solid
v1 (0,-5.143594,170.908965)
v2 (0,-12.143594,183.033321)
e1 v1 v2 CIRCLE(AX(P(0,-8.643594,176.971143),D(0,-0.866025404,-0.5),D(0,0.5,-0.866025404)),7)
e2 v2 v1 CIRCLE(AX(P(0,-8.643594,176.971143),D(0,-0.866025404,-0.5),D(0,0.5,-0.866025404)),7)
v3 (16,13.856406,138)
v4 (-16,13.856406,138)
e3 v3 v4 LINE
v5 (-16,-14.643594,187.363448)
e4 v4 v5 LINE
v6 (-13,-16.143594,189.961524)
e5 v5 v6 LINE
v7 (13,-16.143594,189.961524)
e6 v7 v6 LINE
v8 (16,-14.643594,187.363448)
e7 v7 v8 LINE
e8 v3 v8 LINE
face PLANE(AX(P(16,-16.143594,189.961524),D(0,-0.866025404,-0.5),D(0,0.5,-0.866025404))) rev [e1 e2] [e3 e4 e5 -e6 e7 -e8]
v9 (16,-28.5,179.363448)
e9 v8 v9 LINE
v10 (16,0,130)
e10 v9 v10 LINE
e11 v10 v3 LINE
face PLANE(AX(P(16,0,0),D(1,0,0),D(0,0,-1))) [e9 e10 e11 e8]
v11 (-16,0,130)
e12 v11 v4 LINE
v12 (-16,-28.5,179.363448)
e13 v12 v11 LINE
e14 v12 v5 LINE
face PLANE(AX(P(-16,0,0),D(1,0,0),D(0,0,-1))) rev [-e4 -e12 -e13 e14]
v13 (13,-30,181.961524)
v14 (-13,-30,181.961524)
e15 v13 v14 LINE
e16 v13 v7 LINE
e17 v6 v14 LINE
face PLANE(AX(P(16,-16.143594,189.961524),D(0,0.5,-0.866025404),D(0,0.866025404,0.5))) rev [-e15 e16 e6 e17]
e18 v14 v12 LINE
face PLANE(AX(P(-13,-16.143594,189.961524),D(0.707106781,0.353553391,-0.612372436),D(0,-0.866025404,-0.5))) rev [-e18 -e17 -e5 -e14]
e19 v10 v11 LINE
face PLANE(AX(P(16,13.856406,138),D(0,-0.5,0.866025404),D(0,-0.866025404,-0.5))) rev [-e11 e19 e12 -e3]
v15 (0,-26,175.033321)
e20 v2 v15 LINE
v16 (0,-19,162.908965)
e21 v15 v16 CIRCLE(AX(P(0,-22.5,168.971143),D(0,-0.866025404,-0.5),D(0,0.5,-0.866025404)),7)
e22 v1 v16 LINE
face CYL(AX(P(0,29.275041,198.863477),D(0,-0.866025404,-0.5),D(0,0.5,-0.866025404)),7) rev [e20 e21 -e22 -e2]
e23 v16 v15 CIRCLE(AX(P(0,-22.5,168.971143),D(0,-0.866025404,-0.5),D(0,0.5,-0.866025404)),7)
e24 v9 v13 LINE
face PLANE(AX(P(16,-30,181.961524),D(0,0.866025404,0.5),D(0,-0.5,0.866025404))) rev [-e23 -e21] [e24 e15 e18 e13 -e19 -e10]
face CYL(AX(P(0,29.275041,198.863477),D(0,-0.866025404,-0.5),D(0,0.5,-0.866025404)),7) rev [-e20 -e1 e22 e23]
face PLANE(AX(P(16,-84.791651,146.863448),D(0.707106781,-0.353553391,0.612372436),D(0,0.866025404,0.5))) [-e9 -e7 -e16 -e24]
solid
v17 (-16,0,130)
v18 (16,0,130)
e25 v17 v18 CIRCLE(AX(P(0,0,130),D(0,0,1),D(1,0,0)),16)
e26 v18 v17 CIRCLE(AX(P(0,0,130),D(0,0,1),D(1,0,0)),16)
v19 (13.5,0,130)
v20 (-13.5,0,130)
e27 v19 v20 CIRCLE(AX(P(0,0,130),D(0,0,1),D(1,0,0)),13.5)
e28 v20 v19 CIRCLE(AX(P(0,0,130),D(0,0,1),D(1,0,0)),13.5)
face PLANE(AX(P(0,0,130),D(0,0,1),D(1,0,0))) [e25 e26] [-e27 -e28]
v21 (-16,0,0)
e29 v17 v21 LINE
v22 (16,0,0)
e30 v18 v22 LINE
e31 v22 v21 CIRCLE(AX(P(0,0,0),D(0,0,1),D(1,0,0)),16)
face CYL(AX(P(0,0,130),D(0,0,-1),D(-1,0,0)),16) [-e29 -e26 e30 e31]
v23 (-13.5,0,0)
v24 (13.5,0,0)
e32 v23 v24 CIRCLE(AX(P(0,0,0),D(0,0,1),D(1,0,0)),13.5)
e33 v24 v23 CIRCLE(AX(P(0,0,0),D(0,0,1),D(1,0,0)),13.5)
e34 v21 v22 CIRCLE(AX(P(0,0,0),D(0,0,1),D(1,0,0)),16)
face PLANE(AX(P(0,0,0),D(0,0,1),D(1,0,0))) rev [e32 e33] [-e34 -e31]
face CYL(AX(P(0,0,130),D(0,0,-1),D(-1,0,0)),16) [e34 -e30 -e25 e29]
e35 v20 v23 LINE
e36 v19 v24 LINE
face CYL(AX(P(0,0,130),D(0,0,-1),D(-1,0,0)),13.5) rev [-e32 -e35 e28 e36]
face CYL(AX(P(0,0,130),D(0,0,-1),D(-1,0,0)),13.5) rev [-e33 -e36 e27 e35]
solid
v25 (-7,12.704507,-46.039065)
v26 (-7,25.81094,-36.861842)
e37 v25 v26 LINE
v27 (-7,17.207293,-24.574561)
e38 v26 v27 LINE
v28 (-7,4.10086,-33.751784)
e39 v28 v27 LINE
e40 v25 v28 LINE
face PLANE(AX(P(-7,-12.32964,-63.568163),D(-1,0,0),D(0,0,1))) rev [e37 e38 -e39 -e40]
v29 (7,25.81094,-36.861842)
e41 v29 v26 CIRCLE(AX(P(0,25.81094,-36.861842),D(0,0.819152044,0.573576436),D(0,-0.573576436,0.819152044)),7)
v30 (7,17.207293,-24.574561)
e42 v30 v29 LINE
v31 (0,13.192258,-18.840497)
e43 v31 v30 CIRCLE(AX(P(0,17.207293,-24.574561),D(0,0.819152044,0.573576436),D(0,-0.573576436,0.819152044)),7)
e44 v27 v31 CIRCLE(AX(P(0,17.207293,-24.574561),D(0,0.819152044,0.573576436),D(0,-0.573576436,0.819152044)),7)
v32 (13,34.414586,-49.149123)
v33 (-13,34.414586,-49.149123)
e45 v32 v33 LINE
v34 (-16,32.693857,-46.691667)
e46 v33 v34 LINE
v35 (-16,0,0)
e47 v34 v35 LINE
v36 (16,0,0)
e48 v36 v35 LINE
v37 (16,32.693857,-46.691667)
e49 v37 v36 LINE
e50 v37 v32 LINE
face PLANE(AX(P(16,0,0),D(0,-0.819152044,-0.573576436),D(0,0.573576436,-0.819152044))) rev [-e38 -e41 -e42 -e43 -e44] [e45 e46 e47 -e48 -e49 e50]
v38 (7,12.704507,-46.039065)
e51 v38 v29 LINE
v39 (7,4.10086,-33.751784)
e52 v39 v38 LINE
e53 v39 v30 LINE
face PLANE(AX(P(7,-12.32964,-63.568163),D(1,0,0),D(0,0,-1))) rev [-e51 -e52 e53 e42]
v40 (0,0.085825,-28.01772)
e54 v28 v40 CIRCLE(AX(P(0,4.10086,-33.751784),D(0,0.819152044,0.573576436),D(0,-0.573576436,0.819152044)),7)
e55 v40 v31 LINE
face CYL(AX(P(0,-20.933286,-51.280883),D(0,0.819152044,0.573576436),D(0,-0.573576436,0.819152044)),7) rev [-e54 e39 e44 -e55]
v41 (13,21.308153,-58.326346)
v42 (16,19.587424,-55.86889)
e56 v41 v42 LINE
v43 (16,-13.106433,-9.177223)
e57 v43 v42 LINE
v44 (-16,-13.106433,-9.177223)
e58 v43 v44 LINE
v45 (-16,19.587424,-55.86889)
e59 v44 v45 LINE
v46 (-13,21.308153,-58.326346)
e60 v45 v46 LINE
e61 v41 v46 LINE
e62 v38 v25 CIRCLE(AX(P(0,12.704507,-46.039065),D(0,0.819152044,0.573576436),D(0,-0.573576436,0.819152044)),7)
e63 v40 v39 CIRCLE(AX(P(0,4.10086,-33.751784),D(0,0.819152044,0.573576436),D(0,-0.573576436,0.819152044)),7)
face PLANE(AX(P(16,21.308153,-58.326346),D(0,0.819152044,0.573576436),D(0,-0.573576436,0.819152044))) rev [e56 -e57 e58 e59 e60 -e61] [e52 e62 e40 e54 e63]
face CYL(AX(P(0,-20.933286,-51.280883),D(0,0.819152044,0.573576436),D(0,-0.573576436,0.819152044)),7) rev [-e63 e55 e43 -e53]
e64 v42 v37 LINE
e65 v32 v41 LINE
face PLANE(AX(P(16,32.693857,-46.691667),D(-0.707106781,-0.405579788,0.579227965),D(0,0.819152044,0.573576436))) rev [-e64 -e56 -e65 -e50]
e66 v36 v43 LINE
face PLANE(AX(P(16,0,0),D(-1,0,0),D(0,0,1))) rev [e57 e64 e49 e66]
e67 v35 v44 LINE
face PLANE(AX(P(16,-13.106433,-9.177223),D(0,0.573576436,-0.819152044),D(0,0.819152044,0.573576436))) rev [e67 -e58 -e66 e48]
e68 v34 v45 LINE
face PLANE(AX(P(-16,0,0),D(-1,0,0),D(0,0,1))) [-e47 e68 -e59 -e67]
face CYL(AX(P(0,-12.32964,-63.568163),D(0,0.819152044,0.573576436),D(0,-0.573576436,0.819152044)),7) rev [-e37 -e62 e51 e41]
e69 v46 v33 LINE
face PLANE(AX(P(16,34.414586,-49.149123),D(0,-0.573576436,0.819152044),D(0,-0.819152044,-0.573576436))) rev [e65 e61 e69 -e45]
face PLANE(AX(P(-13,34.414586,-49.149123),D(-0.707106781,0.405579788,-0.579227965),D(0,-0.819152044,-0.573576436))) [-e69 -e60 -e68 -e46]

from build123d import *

# Parameters (mm, degrees)
SKETCH_1_R          = 16
SKETCH_1_R_2        = 13.5
EXTRUDE_1_DEPTH     = 130
EXTRUDE_2_DEPTH     = 16
CUT_EXTRUDE_1_DEPTH = 136.426599093
EXTRUDE_3_DEPTH     = 16
SKETCH_5_R          = 7
CUT_EXTRUDE_2_DEPTH = 181.267525325
CHAMFER_1_SIZE      = 3
CHAMFER_2_SIZE      = 3


with BuildPart() as part:
    # 草图1 → 凸台-拉伸1 (new body)
    with BuildSketch(Plane.XY):
        Circle(SKETCH_1_R)
        Circle(SKETCH_1_R_2, mode=Mode.SUBTRACT)
    extrude(amount=EXTRUDE_1_DEPTH)


with BuildPart() as body_2:
    # 草图2 → 凸台-拉伸2 (new, symmetric)
    with BuildSketch(Plane(origin=(0, 0, 0), x_dir=(0, 0, -1), z_dir=(1, 0, 0))):
        Polygon((0, 0), (49.149122657, 34.414586181), (58.326345639, 21.308153472), (9.177222982, -13.106432709), align=None)
    extrude(amount=EXTRUDE_2_DEPTH, both=True)

    # 草图3 → 切除-拉伸1 (cut, through all)
    with BuildSketch(Plane(origin=(0, 0, 0), x_dir=(1, 0, 0), z_dir=(0, 0.8191520442889908, 0.5735764363510477))):
        with BuildLine():
            Line((7, 45), (7, 30))
            ThreePointArc((7, 30), (0, 23), (-7, 30))
            Line((-7, 30), (-7, 45))
            ThreePointArc((-7, 45), (0, 52), (7, 45))
        make_face()
    extrude(amount=-CUT_EXTRUDE_1_DEPTH, mode=Mode.SUBTRACT)

    # 倒角2
    chamfer_2_edges = [body_2.edges().sort_by_distance(p)[0] for p in [
        (16, 27.861369827, -53.737734148),
        (-16, 27.861369827, -53.737734148),
    ]]
    chamfer(chamfer_2_edges, length=CHAMFER_2_SIZE)


with BuildPart() as body_3:
    # 草图4 → 凸台-拉伸3 (new, symmetric)
    with BuildSketch(Plane(origin=(0, 0, 0), x_dir=(0, 0, -1), z_dir=(1, 0, 0))):
        Polygon((-189.961524227, -16.143593539), (-181.961524227, -30), (-130, 0), (-138, 13.856406461), align=None)
    extrude(amount=EXTRUDE_3_DEPTH, both=True)

    # 草图5 → 切除-拉伸2 (cut, through all)
    with BuildSketch(Plane(origin=(0, 56.291651246, 32.5), x_dir=(1, 0, 0), z_dir=(0, -0.8660254037844374, -0.5000000000000021))):
        with Locations(Location((0, 157.583302492, 0), (0, 0, 270))):
            Circle(SKETCH_5_R)
    extrude(amount=-CUT_EXTRUDE_2_DEPTH, mode=Mode.SUBTRACT)

    # 倒角1
    chamfer_1_edges = [body_3.edges().sort_by_distance(p)[0] for p in [
        (16, -23.07179677, 185.961524227),
        (-16, -23.07179677, 185.961524227),
    ]]
    chamfer(chamfer_1_edges, length=CHAMFER_1_SIZE)


solid = Compound([part.part, body_2.part, body_3.part])
